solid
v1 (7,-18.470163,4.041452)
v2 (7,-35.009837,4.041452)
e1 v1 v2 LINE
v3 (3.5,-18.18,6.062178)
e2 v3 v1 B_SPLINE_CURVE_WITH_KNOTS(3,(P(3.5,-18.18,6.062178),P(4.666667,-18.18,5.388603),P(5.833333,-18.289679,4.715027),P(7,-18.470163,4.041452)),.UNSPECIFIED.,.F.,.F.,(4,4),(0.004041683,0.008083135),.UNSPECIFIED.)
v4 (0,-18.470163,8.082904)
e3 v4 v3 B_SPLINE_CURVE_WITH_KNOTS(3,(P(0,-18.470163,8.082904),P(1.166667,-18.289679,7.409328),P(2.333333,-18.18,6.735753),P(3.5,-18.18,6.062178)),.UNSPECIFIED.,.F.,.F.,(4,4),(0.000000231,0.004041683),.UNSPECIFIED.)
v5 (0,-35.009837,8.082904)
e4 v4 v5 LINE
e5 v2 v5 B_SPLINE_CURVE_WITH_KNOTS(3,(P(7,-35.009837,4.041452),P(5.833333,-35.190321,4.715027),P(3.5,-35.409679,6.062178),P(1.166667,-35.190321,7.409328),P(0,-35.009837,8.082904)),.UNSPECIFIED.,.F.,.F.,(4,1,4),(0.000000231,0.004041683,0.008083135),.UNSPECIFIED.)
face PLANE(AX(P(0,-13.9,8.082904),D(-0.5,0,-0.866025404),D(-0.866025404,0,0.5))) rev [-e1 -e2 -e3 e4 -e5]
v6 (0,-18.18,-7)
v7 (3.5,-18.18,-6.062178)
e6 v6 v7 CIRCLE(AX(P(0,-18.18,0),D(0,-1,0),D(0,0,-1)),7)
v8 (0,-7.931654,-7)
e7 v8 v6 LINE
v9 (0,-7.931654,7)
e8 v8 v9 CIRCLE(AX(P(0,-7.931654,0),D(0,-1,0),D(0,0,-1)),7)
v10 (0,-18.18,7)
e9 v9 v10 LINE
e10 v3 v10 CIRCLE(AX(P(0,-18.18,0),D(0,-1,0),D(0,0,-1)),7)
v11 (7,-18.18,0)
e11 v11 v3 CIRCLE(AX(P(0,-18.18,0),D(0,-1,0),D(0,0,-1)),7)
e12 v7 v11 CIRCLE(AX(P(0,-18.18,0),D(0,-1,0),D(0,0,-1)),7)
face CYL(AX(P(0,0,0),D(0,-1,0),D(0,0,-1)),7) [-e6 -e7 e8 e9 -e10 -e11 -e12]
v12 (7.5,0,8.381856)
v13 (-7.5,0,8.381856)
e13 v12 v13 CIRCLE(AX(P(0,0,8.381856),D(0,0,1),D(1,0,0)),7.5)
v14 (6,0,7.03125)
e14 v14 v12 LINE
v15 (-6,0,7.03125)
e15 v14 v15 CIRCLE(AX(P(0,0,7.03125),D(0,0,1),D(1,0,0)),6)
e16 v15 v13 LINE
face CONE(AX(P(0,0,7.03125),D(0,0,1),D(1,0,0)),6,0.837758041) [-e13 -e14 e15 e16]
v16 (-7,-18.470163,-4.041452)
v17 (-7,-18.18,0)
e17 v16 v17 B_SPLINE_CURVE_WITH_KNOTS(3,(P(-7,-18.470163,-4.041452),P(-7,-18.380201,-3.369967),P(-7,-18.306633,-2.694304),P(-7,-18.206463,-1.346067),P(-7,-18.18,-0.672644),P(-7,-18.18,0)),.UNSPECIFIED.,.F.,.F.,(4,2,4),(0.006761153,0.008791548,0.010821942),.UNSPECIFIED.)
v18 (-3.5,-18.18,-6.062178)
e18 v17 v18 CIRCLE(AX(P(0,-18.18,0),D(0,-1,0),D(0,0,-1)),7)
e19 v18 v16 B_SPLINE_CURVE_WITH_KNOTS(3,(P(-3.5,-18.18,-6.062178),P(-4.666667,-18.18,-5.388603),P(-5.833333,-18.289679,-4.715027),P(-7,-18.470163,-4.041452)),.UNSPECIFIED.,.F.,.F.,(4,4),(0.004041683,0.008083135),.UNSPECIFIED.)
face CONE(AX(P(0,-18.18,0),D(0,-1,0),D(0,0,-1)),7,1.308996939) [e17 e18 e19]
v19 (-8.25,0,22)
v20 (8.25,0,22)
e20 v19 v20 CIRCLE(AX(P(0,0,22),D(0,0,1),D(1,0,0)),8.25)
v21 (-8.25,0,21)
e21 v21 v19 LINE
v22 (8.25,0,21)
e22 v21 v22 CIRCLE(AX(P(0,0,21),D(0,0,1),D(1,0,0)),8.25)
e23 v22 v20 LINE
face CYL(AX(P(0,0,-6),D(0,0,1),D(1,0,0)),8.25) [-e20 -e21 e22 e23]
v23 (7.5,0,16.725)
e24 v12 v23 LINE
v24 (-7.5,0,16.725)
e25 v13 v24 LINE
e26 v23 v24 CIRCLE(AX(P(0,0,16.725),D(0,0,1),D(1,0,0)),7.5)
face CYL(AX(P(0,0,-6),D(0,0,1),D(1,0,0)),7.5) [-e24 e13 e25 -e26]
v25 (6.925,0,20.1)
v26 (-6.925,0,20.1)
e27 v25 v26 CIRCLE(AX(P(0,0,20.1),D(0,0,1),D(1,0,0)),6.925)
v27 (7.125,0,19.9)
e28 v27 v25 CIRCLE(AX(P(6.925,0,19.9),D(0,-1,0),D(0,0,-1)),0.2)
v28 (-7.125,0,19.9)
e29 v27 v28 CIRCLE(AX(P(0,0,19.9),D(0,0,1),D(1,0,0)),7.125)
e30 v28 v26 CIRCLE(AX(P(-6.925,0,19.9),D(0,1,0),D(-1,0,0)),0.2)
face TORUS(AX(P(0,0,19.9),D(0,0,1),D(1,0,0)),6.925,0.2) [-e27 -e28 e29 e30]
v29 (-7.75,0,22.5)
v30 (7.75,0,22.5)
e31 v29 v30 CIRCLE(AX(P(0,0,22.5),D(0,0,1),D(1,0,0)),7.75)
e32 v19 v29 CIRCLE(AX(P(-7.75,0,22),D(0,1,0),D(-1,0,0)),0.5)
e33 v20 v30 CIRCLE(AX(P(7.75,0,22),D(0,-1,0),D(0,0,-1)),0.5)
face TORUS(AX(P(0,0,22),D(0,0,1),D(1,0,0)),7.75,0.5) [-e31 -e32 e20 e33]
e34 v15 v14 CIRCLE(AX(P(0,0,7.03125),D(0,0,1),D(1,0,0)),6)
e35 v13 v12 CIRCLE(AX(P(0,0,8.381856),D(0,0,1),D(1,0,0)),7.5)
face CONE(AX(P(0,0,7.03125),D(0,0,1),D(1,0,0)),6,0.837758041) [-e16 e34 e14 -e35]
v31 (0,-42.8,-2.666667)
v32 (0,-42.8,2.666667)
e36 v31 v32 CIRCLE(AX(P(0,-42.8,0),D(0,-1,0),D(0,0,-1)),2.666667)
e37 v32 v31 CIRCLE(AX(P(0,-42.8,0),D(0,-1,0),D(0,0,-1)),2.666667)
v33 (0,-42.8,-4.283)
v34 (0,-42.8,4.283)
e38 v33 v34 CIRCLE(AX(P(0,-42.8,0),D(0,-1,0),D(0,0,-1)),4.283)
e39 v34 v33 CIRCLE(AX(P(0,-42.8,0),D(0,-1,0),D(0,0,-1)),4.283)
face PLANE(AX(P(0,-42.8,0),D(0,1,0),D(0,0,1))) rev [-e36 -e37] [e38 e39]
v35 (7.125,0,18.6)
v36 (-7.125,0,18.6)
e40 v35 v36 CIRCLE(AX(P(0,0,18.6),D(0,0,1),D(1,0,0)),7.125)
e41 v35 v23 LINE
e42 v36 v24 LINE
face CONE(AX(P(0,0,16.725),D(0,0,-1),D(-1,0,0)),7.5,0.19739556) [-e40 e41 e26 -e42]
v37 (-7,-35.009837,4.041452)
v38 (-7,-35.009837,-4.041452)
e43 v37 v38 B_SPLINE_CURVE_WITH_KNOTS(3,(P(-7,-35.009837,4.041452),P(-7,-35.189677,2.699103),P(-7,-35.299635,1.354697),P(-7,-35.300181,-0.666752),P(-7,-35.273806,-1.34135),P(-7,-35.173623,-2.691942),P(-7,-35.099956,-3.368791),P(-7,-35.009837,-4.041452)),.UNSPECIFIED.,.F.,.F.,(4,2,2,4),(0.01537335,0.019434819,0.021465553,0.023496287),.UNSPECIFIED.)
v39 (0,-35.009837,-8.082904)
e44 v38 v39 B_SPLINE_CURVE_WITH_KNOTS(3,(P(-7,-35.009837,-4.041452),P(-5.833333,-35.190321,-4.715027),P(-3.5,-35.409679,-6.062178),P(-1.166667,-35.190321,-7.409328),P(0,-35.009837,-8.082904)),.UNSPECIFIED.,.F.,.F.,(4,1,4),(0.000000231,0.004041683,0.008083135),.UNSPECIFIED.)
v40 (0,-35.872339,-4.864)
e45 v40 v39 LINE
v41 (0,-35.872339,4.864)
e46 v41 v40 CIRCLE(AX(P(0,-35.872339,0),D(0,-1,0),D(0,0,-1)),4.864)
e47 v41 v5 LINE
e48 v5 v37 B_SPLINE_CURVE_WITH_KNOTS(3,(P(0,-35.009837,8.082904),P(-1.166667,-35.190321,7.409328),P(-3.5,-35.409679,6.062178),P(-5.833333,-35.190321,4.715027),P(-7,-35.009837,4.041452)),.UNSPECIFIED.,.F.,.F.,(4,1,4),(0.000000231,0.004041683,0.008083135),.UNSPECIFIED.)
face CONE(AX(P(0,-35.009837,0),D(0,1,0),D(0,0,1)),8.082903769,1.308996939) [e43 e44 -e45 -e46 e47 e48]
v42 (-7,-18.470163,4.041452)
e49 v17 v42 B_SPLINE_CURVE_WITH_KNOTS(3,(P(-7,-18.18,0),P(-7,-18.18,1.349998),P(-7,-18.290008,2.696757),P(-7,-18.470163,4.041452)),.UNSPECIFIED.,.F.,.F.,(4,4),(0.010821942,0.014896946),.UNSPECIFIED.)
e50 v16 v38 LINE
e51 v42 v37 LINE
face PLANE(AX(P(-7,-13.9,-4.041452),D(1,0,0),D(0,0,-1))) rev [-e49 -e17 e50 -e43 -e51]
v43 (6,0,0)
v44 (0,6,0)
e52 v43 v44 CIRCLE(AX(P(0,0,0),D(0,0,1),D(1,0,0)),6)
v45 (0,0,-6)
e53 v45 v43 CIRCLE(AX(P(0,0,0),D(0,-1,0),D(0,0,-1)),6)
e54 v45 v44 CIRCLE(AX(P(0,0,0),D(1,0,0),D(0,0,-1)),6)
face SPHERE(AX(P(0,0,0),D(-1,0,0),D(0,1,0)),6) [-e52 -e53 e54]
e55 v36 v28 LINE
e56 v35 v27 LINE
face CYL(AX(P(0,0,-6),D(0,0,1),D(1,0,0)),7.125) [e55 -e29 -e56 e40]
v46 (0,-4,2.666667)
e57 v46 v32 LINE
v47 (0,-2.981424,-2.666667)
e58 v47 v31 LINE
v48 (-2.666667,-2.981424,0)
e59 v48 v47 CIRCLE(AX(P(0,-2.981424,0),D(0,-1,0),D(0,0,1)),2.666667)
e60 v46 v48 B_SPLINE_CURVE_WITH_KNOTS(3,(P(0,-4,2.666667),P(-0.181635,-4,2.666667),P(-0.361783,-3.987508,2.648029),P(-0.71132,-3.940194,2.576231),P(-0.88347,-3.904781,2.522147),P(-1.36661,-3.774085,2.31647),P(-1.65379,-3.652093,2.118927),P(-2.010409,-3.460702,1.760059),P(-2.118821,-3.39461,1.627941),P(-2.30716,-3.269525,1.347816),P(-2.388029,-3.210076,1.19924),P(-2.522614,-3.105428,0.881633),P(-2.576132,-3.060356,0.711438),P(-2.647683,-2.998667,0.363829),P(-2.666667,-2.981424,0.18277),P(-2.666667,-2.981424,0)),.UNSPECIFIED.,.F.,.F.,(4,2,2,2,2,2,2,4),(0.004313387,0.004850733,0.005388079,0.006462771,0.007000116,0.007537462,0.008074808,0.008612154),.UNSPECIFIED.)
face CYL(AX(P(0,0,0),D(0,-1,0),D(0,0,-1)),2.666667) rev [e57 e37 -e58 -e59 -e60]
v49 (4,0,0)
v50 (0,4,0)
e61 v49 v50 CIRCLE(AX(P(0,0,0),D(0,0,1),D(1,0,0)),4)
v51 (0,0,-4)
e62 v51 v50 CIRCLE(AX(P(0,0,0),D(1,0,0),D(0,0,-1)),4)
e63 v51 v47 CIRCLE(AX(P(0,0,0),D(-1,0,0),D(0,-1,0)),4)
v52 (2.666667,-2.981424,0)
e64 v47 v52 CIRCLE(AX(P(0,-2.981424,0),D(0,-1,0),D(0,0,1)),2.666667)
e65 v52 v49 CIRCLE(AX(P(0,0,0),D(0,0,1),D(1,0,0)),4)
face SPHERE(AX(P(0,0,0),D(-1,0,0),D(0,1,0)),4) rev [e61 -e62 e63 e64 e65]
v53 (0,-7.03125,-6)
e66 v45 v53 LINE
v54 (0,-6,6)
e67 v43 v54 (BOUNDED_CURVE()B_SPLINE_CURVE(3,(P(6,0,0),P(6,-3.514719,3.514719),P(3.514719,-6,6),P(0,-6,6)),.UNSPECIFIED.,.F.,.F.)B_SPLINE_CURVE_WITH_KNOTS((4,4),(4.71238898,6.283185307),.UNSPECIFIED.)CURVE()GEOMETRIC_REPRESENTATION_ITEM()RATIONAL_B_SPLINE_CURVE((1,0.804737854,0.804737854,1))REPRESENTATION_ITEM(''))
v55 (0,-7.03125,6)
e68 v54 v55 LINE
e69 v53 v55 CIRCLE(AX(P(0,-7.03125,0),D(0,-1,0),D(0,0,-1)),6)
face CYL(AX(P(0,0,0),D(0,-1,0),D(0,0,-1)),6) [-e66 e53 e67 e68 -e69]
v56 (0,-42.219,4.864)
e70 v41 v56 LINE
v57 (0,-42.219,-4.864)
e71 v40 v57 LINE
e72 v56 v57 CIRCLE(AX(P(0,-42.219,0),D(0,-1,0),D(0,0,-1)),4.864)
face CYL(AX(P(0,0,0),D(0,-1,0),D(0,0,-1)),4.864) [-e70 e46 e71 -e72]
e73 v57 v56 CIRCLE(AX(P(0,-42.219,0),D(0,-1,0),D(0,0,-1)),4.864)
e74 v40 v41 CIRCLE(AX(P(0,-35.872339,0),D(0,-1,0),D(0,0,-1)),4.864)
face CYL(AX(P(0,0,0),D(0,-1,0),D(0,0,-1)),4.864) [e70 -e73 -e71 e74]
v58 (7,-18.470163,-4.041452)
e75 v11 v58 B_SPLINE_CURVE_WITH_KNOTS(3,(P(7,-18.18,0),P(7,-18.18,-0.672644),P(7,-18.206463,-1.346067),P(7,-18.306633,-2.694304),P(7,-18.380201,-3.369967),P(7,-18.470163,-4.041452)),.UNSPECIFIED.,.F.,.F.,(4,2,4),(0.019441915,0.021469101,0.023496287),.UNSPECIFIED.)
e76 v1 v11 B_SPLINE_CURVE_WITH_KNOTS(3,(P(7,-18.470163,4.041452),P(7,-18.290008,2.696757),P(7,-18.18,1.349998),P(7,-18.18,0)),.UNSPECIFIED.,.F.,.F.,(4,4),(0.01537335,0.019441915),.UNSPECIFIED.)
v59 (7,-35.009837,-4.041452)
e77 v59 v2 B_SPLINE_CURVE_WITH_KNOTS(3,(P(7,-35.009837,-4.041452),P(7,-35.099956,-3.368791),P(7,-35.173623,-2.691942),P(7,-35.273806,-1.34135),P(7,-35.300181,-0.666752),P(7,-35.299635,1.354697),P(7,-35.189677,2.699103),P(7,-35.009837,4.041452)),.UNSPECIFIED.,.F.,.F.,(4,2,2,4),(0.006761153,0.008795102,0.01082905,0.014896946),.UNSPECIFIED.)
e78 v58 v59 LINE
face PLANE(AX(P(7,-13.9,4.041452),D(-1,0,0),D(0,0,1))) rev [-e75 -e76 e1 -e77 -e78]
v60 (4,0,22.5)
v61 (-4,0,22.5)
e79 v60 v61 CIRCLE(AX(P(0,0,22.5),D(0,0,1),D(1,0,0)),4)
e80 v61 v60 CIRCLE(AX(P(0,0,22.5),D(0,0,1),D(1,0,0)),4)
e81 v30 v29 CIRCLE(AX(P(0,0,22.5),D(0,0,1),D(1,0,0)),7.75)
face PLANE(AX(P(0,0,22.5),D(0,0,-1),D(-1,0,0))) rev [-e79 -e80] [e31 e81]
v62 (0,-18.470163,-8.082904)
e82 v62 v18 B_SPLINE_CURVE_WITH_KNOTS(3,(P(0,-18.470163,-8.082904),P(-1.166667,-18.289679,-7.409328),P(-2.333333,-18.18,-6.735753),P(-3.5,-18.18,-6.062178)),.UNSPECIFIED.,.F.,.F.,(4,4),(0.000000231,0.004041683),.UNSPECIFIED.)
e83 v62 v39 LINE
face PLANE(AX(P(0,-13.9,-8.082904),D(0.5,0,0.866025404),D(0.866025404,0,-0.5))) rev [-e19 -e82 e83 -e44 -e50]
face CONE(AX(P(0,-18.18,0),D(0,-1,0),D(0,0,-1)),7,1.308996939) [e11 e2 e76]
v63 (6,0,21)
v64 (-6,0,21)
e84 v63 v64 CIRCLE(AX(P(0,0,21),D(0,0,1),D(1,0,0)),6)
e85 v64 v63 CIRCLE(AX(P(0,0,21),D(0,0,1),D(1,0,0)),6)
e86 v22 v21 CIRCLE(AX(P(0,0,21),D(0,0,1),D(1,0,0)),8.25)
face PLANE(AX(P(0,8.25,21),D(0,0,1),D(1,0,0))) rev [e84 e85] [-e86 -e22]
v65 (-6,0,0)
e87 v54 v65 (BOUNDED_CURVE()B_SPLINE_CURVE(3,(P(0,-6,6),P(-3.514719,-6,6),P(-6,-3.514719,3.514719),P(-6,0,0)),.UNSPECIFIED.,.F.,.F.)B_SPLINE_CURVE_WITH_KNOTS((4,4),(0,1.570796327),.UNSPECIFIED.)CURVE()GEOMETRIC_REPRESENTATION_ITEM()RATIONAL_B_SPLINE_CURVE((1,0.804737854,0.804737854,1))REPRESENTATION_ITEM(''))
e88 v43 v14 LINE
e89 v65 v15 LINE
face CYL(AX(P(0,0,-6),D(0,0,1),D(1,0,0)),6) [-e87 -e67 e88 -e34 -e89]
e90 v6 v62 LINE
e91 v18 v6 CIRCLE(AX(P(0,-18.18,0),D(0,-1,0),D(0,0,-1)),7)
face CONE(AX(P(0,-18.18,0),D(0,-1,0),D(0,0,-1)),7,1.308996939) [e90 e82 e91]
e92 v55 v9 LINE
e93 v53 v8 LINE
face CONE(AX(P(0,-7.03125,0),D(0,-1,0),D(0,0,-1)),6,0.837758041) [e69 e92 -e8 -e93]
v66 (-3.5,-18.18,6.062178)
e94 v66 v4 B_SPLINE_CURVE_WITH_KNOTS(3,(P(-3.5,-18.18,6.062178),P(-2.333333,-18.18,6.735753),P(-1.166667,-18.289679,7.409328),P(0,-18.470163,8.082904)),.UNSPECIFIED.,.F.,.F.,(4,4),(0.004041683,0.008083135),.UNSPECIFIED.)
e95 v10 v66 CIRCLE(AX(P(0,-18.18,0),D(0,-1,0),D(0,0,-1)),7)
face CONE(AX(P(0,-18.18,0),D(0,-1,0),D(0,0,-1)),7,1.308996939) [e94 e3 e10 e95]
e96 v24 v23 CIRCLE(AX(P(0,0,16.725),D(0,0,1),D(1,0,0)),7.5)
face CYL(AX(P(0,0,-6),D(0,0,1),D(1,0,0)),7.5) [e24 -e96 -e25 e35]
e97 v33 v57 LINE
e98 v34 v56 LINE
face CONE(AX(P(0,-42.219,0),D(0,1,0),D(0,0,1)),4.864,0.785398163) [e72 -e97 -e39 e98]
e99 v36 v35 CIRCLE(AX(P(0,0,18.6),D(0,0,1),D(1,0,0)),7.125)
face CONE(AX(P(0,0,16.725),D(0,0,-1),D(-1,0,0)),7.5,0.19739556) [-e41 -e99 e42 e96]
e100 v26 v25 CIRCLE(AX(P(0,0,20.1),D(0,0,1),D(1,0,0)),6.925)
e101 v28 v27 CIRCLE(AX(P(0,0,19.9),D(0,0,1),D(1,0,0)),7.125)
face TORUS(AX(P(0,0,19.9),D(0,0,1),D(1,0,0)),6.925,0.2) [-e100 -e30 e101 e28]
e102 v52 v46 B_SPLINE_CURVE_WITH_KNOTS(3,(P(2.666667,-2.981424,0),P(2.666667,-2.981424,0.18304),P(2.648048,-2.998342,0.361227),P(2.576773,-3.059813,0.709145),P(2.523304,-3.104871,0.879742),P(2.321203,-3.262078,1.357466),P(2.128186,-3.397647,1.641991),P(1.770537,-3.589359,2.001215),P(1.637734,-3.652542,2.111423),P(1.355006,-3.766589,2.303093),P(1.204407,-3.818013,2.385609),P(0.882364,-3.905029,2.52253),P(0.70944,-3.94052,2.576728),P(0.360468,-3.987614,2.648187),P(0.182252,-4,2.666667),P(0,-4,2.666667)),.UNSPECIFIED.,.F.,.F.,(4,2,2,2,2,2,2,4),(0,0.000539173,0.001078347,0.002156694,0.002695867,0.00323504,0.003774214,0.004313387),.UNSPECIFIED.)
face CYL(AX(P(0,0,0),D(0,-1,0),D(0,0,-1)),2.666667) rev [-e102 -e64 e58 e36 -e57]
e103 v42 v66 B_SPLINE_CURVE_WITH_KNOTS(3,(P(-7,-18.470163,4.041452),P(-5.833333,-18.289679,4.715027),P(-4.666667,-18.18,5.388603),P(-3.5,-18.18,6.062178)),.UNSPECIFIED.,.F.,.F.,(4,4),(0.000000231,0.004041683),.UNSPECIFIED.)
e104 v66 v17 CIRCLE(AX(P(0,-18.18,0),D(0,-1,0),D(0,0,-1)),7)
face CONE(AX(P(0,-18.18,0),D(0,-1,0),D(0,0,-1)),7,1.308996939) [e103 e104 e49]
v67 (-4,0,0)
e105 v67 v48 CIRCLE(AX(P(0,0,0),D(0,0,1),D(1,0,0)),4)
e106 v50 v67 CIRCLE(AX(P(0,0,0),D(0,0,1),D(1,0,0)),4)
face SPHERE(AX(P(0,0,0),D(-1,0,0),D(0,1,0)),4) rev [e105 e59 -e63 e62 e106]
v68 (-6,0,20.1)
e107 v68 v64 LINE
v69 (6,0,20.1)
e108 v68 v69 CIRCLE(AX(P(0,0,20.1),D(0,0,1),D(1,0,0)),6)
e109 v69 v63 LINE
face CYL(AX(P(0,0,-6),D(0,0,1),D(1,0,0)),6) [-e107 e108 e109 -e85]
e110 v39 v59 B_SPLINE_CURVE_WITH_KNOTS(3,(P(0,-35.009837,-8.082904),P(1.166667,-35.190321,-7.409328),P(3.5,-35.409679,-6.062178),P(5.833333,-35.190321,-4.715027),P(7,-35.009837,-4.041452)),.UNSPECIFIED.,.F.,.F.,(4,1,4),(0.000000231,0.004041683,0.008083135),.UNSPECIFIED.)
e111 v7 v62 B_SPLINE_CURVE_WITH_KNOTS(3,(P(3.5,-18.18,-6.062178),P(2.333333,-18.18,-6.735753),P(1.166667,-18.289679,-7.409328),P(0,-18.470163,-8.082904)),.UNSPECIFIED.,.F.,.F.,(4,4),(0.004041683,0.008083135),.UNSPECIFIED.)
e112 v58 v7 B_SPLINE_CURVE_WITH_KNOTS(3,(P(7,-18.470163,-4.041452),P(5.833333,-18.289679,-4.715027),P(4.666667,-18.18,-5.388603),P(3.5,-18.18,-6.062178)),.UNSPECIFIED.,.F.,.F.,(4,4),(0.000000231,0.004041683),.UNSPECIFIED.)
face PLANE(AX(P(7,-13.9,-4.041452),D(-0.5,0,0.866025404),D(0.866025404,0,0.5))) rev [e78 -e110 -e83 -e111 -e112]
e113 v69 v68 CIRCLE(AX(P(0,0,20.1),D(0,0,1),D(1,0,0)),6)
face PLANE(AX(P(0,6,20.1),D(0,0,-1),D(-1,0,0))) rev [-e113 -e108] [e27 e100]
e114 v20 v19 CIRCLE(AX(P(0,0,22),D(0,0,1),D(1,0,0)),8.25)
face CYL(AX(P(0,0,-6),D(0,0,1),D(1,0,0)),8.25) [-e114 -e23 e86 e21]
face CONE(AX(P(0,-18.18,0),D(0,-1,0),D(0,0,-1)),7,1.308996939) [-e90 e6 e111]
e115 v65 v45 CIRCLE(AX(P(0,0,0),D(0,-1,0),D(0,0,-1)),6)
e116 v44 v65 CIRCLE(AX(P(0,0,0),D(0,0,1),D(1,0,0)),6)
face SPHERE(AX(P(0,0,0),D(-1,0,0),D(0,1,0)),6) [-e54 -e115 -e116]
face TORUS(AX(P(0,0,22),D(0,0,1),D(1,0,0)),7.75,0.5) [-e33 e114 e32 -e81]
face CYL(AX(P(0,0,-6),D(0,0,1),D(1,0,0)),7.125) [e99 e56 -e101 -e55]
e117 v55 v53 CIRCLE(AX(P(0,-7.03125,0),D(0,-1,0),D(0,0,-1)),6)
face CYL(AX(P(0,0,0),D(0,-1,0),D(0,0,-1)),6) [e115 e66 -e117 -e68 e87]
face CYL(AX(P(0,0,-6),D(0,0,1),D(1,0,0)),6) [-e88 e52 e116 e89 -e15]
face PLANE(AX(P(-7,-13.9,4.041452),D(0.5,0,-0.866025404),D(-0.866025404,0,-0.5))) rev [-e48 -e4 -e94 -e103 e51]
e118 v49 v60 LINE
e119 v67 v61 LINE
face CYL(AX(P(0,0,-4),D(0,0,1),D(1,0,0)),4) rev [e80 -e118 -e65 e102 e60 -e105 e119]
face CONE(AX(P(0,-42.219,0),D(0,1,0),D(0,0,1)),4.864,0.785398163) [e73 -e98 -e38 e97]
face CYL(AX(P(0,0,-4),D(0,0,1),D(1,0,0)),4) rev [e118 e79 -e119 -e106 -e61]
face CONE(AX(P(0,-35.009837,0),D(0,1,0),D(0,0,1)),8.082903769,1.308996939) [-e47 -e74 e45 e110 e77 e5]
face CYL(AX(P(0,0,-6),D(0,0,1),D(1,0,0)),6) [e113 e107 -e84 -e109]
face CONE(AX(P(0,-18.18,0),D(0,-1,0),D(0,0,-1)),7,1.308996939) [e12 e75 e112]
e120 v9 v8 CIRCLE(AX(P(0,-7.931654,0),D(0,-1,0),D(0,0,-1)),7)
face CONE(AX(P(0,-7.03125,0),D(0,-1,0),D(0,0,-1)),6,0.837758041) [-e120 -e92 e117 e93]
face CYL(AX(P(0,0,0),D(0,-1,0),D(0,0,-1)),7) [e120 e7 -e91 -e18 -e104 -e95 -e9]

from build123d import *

# Parameters (mm, degrees)
SKETCH_3_R          = 14
CUT_EXTRUDE_1_DEPTH = 21.4
SKETCH_5_W          = 2.666666667
SKETCH_5_H          = 42.8


with BuildPart() as part:
    # 草图1 → 旋转1 (revolve)
    with BuildSketch(Plane(origin=(0, 0, 0), x_dir=(0, 0, -1), z_dir=(1, 0, 0)), mode=Mode.PRIVATE) as revolve_1_sk:
        with BuildLine():
            Line((-22.5, 0), (-22.5, 7.75))
            ThreePointArc((-22.5, 7.75), (-22.353553391, 8.103553391), (-22, 8.25))
            Line((-22, 8.25), (-21, 8.25))
            Line((-21, 8.25), (-21, 6))
            Line((-21, 6), (-20.1, 6))
            Line((-20.1, 6), (-20.1, 6.925))
            ThreePointArc((-20.1, 6.925), (-20.041421356, 7.066421356), (-19.9, 7.125))
            Line((-19.9, 7.125), (-18.6, 7.125))
            Line((-18.6, 7.125), (-16.725, 7.5))
            Line((-16.725, 7.5), (-8.381856066, 7.5))
            Line((-8.381856066, 7.5), (-7.03125, 6))
            Line((-7.03125, 6), (0, 6))
            ThreePointArc((0, 6), (4.242640687, 4.242640687), (6, 0))
            Line((6, 0), (-22.5, 0))
        make_face()
    revolve(revolve_1_sk.sketch.rotate(Axis((0, 0, -6), (0, 0, 1)), 270), axis=Axis((0, 0, -6), (0, 0, 1)))

    # 草图2 → 旋转2 (revolve)
    with BuildSketch(Plane(origin=(0, 0, 0), x_dir=(0, 0, -1), z_dir=(1, 0, 0)), mode=Mode.PRIVATE) as revolve_2_sk:
        Polygon((0, -42.8), (-4.283, -42.8), (-4.864, -42.219), (-4.864, -35.872339475), (-8.082903769, -35.00983681), (-8.082903769, -18.47016319), (-7, -18.18), (-7, -7.931654044), (-6, -7.03125), (-6, 0), (0, 0), align=None)
    revolve(revolve_2_sk.sketch.rotate(Axis((0, 0, 0), (0, -1, 0)), 180), axis=Axis((0, 0, 0), (0, -1, 0)))

    # 草图3 → 切除-拉伸1 (cut)
    with BuildSketch(Plane(origin=(0, -35.3, 0), x_dir=(1, 0, 0), z_dir=(0, 1, 0))):
        Circle(SKETCH_3_R)
        Polygon((-7, 4.041451884), (-7, -4.041451884), (0, -8.082903769), (7, -4.041451884), (7, 4.041451884), (0, 8.082903769), align=None, mode=Mode.SUBTRACT)
    extrude(amount=CUT_EXTRUDE_1_DEPTH, mode=Mode.SUBTRACT)

    # 草图4 → 切除-旋转1 (revolve, cut)
    with BuildSketch(Plane(origin=(0, 0, 0), x_dir=(0, 0, -1), z_dir=(1, 0, 0)), mode=Mode.PRIVATE) as cut_revolve_1_sk:
        with BuildLine():
            Line((-22.5, 0), (-22.5, 4))
            Line((-22.5, 4), (0, 4))
            ThreePointArc((0, 4), (2.828427125, 2.828427125), (4, 0))
            Line((4, 0), (-22.5, 0))
        make_face()
    revolve(cut_revolve_1_sk.sketch.rotate(Axis((0, 0, -4), (0, 0, 1)), 270), axis=Axis((0, 0, -4), (0, 0, 1)), mode=Mode.SUBTRACT)

    # 草图5 → 切除-旋转2 (revolve, cut)
    with BuildSketch(Plane(origin=(0, 0, 0), x_dir=(0, 0, -1), z_dir=(1, 0, 0)), mode=Mode.PRIVATE) as cut_revolve_2_sk:
        with Locations((-1.333333334, -21.4)):
            Rectangle(SKETCH_5_W, SKETCH_5_H)
    revolve(cut_revolve_2_sk.sketch.rotate(Axis((0, 0, 0), (0, -1, 0)), 180), axis=Axis((0, 0, 0), (0, -1, 0)), mode=Mode.SUBTRACT)


solid = part.part
